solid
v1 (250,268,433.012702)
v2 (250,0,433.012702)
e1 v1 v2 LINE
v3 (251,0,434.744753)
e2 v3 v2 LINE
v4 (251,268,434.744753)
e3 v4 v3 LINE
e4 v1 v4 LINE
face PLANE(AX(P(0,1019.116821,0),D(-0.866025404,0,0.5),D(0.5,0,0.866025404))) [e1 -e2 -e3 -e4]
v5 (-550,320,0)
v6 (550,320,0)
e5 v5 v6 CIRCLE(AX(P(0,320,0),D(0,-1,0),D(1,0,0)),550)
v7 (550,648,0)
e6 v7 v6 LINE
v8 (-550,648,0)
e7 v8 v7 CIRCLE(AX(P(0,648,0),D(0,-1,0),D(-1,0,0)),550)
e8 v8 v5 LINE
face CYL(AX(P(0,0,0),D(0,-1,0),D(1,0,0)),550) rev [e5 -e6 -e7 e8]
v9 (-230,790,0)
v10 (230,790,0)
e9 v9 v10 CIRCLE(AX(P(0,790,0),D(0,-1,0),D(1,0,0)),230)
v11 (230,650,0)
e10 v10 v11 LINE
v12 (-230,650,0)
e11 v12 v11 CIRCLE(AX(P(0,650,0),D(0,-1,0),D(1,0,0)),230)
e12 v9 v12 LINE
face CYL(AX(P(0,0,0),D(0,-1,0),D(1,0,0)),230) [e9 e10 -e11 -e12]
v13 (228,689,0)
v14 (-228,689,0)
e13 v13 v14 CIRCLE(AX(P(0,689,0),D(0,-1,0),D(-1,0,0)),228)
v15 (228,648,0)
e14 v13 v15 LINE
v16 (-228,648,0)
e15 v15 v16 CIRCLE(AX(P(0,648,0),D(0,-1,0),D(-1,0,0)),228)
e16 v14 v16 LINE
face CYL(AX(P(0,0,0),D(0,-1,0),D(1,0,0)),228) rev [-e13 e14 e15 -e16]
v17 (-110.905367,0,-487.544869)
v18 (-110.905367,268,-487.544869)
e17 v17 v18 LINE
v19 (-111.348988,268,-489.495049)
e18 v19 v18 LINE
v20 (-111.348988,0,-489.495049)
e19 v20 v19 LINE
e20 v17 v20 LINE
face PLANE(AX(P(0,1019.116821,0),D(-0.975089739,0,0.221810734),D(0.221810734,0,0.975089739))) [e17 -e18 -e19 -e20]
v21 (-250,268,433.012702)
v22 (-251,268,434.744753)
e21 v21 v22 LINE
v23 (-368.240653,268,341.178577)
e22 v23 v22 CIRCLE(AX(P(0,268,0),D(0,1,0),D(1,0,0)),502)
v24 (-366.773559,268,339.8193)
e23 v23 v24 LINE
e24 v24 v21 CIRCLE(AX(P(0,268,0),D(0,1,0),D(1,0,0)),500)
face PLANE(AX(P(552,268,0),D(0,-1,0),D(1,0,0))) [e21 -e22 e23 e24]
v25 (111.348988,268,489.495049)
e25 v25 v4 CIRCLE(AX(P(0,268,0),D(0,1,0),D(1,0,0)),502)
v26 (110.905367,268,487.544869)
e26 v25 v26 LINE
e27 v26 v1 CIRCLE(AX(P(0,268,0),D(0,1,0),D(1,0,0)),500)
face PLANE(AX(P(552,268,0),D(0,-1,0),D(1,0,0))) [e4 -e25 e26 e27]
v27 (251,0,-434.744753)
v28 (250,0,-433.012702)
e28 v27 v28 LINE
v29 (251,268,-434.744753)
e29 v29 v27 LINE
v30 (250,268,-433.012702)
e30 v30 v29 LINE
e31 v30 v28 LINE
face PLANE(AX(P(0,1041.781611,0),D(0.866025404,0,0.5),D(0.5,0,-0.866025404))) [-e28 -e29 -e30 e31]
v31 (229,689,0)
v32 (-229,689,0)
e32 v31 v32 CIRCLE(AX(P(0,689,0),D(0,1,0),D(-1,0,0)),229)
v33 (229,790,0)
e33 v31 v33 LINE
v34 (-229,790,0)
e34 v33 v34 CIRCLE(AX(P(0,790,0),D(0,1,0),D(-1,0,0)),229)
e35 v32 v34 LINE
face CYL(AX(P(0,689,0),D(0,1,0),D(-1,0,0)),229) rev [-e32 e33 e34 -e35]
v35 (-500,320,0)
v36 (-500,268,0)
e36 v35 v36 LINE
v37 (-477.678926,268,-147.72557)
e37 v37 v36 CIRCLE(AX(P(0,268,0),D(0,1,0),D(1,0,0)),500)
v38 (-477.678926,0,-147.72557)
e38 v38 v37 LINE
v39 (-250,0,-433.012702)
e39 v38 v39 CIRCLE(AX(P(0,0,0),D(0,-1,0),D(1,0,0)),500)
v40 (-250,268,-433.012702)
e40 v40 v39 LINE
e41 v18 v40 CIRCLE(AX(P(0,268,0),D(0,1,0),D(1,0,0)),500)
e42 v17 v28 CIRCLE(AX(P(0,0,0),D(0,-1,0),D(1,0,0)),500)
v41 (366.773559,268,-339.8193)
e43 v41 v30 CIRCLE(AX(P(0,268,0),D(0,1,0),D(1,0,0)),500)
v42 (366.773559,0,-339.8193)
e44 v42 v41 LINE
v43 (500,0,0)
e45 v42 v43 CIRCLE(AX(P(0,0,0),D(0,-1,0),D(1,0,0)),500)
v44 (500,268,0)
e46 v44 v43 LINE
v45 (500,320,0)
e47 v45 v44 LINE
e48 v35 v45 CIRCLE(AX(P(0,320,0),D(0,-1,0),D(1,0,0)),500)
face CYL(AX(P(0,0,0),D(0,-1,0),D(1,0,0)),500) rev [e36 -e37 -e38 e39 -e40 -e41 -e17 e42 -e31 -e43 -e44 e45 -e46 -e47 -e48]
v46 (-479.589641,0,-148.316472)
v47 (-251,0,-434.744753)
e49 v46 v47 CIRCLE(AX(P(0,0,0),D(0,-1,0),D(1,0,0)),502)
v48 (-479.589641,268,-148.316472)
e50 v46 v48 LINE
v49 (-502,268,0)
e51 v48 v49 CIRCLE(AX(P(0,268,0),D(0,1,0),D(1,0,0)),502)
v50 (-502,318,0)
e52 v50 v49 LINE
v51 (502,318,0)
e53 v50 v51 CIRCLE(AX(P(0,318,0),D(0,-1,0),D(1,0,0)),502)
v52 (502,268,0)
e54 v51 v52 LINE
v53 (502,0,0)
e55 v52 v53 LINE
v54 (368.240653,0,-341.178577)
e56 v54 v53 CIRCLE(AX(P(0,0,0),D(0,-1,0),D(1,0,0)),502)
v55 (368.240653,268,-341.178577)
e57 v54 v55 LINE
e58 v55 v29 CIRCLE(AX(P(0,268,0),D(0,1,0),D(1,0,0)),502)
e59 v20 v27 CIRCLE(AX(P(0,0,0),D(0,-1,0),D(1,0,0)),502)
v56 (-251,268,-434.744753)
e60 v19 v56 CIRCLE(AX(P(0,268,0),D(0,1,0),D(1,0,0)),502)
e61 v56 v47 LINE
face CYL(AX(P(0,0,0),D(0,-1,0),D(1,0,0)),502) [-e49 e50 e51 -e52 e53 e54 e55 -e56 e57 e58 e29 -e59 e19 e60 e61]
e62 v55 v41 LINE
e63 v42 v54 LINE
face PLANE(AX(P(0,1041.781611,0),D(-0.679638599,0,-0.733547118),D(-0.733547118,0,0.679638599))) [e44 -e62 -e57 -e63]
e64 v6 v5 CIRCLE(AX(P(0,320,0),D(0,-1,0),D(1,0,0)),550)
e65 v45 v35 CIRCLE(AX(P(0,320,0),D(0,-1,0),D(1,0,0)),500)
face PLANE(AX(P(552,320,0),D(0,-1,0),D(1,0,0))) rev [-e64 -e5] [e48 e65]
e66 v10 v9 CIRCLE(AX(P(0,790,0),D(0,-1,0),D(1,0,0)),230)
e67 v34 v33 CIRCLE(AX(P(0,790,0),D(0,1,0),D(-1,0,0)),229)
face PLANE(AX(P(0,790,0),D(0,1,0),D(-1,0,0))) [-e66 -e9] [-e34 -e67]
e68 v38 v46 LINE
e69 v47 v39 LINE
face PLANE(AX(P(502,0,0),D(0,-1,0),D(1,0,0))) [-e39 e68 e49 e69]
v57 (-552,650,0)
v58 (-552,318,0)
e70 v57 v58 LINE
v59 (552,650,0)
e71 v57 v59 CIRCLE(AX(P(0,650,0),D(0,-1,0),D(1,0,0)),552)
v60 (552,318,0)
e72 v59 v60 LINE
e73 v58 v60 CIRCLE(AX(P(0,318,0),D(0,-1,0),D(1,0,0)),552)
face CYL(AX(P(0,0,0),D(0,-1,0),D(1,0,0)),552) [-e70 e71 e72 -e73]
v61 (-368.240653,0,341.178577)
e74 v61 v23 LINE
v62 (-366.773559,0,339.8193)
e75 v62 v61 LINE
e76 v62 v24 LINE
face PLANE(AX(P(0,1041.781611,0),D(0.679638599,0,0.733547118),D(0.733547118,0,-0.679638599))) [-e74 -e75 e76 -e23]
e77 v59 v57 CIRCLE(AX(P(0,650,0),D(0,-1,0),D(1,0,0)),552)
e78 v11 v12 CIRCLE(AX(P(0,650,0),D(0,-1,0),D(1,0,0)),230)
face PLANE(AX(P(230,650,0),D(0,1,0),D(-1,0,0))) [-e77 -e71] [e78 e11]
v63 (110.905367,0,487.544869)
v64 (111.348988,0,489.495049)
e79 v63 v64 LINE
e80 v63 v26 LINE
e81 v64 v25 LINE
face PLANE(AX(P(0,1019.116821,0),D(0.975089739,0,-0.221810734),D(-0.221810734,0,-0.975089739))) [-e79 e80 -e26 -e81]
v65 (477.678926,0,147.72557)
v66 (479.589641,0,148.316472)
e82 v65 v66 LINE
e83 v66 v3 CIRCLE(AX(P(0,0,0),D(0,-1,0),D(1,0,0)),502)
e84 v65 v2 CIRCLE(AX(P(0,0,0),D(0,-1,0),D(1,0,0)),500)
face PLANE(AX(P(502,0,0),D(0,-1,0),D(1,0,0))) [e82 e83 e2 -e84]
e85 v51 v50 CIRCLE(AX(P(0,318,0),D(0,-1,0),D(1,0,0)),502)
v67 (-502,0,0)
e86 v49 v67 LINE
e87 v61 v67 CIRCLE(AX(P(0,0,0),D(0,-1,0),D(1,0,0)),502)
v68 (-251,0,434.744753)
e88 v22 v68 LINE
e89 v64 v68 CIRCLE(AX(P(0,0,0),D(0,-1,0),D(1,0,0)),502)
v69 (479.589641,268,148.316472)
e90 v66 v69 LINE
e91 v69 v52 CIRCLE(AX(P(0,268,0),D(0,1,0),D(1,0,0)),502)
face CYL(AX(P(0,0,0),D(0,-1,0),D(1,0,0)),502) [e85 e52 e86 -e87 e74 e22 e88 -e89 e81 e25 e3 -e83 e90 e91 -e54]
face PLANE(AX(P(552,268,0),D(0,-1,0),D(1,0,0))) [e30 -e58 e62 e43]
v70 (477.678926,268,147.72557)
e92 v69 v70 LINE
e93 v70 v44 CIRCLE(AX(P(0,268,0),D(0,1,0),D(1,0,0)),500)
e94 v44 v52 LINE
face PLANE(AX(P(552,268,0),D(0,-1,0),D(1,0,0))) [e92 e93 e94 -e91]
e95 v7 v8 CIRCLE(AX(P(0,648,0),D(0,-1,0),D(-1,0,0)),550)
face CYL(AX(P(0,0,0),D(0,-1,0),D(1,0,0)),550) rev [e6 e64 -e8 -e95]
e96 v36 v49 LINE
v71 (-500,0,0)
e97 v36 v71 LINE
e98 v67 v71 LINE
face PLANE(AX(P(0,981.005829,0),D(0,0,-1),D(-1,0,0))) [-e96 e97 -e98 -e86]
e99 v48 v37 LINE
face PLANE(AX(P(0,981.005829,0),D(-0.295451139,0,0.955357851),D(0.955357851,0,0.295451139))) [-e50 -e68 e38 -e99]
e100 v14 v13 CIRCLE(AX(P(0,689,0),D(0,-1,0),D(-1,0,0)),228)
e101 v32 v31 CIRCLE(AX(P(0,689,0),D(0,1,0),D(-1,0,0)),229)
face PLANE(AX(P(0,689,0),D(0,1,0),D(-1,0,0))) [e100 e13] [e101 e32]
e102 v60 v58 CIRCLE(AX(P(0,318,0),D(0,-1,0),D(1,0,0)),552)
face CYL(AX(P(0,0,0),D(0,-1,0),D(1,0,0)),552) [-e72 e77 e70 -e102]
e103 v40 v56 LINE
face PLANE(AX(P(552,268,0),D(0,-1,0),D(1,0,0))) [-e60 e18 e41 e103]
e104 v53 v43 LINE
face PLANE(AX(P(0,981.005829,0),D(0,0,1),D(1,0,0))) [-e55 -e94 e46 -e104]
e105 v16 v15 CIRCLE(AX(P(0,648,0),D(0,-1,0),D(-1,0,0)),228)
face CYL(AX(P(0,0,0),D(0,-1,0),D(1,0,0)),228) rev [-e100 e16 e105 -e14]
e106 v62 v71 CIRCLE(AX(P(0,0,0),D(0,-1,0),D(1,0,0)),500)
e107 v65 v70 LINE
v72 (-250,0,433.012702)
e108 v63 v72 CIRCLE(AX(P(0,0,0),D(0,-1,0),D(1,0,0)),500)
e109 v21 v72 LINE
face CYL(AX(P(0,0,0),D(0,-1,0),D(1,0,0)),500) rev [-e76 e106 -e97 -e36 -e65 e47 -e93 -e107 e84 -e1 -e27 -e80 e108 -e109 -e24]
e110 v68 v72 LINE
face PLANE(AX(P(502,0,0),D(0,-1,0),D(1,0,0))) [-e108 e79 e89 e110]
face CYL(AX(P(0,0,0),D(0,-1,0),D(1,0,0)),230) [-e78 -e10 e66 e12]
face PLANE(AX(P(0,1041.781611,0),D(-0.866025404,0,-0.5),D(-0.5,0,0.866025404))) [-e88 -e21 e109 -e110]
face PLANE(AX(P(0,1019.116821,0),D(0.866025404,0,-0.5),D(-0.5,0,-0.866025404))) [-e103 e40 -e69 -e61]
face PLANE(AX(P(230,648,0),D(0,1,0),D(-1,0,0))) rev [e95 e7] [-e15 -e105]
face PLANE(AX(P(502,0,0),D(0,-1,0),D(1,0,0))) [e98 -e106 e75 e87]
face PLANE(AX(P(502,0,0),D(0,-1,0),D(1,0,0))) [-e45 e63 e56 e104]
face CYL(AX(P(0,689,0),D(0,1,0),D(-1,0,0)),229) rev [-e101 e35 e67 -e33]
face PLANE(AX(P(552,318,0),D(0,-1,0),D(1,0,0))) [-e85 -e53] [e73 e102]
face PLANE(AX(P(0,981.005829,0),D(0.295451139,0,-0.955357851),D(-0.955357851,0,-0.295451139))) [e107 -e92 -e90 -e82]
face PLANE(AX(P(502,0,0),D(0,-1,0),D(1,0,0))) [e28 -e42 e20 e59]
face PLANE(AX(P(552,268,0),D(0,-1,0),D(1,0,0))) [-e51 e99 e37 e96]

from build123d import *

# Parameters (mm, degrees)
SHELL1_T           = -2
SKETCH2_R          = 229
CUT_EXTRUDE1_DEPTH = 101
CUT_EXTRUDE2_DEPTH = 268
CIRPATTERN1_COUNT  = 6


with BuildPart() as part:
    # Sketch1 → Revolve1 (revolve)
    with BuildSketch(Plane.XY):
        Polygon((0, 0), (0, 790), (230, 790), (230, 650), (552, 650), (552, 318), (502, 318), (502, 0), align=None)
    revolve(axis=Axis((0, 0, 0), (0, 1, 0)))

    # Shell1
    shell1_openings = [part.faces().sort_by_distance(p)[0] for p in [
        (0, 0, 0),
    ]]
    offset(amount=SHELL1_T, openings=shell1_openings, kind=Kind.INTERSECTION)

    # Sketch2 → Cut-Extrude1 (cut)
    with BuildSketch(Plane(origin=(0, 790, 0), x_dir=(1, 0, 0), z_dir=(0, 1, 0))):
        with Locations(Location((0, 0, 0), (0, 0, 180))):
            Circle(SKETCH2_R)
    extrude(amount=-CUT_EXTRUDE1_DEPTH, mode=Mode.SUBTRACT)

    # Sketch3 → Cut-Extrude2 (cut)
    with BuildSketch(Plane(origin=(0, 0, 0), x_dir=(1, 0, 0), z_dir=(0, 1, 0))):
        Polygon((0, 0), (635.384163394, 0), (612.361562027, -189.37712274), align=None)
    cut_extrude2 = extrude(amount=CUT_EXTRUDE2_DEPTH, mode=Mode.SUBTRACT)

    # CirPattern1: Cut-Extrude2 ×6 about axis
    cirpattern1_axis = Axis((0, 0, 0), (0, 1, 0))
    for i in range(1, CIRPATTERN1_COUNT):
        add(cut_extrude2.rotate(cirpattern1_axis, i * 360 / CIRPATTERN1_COUNT), mode=Mode.SUBTRACT)


solid = part.part
